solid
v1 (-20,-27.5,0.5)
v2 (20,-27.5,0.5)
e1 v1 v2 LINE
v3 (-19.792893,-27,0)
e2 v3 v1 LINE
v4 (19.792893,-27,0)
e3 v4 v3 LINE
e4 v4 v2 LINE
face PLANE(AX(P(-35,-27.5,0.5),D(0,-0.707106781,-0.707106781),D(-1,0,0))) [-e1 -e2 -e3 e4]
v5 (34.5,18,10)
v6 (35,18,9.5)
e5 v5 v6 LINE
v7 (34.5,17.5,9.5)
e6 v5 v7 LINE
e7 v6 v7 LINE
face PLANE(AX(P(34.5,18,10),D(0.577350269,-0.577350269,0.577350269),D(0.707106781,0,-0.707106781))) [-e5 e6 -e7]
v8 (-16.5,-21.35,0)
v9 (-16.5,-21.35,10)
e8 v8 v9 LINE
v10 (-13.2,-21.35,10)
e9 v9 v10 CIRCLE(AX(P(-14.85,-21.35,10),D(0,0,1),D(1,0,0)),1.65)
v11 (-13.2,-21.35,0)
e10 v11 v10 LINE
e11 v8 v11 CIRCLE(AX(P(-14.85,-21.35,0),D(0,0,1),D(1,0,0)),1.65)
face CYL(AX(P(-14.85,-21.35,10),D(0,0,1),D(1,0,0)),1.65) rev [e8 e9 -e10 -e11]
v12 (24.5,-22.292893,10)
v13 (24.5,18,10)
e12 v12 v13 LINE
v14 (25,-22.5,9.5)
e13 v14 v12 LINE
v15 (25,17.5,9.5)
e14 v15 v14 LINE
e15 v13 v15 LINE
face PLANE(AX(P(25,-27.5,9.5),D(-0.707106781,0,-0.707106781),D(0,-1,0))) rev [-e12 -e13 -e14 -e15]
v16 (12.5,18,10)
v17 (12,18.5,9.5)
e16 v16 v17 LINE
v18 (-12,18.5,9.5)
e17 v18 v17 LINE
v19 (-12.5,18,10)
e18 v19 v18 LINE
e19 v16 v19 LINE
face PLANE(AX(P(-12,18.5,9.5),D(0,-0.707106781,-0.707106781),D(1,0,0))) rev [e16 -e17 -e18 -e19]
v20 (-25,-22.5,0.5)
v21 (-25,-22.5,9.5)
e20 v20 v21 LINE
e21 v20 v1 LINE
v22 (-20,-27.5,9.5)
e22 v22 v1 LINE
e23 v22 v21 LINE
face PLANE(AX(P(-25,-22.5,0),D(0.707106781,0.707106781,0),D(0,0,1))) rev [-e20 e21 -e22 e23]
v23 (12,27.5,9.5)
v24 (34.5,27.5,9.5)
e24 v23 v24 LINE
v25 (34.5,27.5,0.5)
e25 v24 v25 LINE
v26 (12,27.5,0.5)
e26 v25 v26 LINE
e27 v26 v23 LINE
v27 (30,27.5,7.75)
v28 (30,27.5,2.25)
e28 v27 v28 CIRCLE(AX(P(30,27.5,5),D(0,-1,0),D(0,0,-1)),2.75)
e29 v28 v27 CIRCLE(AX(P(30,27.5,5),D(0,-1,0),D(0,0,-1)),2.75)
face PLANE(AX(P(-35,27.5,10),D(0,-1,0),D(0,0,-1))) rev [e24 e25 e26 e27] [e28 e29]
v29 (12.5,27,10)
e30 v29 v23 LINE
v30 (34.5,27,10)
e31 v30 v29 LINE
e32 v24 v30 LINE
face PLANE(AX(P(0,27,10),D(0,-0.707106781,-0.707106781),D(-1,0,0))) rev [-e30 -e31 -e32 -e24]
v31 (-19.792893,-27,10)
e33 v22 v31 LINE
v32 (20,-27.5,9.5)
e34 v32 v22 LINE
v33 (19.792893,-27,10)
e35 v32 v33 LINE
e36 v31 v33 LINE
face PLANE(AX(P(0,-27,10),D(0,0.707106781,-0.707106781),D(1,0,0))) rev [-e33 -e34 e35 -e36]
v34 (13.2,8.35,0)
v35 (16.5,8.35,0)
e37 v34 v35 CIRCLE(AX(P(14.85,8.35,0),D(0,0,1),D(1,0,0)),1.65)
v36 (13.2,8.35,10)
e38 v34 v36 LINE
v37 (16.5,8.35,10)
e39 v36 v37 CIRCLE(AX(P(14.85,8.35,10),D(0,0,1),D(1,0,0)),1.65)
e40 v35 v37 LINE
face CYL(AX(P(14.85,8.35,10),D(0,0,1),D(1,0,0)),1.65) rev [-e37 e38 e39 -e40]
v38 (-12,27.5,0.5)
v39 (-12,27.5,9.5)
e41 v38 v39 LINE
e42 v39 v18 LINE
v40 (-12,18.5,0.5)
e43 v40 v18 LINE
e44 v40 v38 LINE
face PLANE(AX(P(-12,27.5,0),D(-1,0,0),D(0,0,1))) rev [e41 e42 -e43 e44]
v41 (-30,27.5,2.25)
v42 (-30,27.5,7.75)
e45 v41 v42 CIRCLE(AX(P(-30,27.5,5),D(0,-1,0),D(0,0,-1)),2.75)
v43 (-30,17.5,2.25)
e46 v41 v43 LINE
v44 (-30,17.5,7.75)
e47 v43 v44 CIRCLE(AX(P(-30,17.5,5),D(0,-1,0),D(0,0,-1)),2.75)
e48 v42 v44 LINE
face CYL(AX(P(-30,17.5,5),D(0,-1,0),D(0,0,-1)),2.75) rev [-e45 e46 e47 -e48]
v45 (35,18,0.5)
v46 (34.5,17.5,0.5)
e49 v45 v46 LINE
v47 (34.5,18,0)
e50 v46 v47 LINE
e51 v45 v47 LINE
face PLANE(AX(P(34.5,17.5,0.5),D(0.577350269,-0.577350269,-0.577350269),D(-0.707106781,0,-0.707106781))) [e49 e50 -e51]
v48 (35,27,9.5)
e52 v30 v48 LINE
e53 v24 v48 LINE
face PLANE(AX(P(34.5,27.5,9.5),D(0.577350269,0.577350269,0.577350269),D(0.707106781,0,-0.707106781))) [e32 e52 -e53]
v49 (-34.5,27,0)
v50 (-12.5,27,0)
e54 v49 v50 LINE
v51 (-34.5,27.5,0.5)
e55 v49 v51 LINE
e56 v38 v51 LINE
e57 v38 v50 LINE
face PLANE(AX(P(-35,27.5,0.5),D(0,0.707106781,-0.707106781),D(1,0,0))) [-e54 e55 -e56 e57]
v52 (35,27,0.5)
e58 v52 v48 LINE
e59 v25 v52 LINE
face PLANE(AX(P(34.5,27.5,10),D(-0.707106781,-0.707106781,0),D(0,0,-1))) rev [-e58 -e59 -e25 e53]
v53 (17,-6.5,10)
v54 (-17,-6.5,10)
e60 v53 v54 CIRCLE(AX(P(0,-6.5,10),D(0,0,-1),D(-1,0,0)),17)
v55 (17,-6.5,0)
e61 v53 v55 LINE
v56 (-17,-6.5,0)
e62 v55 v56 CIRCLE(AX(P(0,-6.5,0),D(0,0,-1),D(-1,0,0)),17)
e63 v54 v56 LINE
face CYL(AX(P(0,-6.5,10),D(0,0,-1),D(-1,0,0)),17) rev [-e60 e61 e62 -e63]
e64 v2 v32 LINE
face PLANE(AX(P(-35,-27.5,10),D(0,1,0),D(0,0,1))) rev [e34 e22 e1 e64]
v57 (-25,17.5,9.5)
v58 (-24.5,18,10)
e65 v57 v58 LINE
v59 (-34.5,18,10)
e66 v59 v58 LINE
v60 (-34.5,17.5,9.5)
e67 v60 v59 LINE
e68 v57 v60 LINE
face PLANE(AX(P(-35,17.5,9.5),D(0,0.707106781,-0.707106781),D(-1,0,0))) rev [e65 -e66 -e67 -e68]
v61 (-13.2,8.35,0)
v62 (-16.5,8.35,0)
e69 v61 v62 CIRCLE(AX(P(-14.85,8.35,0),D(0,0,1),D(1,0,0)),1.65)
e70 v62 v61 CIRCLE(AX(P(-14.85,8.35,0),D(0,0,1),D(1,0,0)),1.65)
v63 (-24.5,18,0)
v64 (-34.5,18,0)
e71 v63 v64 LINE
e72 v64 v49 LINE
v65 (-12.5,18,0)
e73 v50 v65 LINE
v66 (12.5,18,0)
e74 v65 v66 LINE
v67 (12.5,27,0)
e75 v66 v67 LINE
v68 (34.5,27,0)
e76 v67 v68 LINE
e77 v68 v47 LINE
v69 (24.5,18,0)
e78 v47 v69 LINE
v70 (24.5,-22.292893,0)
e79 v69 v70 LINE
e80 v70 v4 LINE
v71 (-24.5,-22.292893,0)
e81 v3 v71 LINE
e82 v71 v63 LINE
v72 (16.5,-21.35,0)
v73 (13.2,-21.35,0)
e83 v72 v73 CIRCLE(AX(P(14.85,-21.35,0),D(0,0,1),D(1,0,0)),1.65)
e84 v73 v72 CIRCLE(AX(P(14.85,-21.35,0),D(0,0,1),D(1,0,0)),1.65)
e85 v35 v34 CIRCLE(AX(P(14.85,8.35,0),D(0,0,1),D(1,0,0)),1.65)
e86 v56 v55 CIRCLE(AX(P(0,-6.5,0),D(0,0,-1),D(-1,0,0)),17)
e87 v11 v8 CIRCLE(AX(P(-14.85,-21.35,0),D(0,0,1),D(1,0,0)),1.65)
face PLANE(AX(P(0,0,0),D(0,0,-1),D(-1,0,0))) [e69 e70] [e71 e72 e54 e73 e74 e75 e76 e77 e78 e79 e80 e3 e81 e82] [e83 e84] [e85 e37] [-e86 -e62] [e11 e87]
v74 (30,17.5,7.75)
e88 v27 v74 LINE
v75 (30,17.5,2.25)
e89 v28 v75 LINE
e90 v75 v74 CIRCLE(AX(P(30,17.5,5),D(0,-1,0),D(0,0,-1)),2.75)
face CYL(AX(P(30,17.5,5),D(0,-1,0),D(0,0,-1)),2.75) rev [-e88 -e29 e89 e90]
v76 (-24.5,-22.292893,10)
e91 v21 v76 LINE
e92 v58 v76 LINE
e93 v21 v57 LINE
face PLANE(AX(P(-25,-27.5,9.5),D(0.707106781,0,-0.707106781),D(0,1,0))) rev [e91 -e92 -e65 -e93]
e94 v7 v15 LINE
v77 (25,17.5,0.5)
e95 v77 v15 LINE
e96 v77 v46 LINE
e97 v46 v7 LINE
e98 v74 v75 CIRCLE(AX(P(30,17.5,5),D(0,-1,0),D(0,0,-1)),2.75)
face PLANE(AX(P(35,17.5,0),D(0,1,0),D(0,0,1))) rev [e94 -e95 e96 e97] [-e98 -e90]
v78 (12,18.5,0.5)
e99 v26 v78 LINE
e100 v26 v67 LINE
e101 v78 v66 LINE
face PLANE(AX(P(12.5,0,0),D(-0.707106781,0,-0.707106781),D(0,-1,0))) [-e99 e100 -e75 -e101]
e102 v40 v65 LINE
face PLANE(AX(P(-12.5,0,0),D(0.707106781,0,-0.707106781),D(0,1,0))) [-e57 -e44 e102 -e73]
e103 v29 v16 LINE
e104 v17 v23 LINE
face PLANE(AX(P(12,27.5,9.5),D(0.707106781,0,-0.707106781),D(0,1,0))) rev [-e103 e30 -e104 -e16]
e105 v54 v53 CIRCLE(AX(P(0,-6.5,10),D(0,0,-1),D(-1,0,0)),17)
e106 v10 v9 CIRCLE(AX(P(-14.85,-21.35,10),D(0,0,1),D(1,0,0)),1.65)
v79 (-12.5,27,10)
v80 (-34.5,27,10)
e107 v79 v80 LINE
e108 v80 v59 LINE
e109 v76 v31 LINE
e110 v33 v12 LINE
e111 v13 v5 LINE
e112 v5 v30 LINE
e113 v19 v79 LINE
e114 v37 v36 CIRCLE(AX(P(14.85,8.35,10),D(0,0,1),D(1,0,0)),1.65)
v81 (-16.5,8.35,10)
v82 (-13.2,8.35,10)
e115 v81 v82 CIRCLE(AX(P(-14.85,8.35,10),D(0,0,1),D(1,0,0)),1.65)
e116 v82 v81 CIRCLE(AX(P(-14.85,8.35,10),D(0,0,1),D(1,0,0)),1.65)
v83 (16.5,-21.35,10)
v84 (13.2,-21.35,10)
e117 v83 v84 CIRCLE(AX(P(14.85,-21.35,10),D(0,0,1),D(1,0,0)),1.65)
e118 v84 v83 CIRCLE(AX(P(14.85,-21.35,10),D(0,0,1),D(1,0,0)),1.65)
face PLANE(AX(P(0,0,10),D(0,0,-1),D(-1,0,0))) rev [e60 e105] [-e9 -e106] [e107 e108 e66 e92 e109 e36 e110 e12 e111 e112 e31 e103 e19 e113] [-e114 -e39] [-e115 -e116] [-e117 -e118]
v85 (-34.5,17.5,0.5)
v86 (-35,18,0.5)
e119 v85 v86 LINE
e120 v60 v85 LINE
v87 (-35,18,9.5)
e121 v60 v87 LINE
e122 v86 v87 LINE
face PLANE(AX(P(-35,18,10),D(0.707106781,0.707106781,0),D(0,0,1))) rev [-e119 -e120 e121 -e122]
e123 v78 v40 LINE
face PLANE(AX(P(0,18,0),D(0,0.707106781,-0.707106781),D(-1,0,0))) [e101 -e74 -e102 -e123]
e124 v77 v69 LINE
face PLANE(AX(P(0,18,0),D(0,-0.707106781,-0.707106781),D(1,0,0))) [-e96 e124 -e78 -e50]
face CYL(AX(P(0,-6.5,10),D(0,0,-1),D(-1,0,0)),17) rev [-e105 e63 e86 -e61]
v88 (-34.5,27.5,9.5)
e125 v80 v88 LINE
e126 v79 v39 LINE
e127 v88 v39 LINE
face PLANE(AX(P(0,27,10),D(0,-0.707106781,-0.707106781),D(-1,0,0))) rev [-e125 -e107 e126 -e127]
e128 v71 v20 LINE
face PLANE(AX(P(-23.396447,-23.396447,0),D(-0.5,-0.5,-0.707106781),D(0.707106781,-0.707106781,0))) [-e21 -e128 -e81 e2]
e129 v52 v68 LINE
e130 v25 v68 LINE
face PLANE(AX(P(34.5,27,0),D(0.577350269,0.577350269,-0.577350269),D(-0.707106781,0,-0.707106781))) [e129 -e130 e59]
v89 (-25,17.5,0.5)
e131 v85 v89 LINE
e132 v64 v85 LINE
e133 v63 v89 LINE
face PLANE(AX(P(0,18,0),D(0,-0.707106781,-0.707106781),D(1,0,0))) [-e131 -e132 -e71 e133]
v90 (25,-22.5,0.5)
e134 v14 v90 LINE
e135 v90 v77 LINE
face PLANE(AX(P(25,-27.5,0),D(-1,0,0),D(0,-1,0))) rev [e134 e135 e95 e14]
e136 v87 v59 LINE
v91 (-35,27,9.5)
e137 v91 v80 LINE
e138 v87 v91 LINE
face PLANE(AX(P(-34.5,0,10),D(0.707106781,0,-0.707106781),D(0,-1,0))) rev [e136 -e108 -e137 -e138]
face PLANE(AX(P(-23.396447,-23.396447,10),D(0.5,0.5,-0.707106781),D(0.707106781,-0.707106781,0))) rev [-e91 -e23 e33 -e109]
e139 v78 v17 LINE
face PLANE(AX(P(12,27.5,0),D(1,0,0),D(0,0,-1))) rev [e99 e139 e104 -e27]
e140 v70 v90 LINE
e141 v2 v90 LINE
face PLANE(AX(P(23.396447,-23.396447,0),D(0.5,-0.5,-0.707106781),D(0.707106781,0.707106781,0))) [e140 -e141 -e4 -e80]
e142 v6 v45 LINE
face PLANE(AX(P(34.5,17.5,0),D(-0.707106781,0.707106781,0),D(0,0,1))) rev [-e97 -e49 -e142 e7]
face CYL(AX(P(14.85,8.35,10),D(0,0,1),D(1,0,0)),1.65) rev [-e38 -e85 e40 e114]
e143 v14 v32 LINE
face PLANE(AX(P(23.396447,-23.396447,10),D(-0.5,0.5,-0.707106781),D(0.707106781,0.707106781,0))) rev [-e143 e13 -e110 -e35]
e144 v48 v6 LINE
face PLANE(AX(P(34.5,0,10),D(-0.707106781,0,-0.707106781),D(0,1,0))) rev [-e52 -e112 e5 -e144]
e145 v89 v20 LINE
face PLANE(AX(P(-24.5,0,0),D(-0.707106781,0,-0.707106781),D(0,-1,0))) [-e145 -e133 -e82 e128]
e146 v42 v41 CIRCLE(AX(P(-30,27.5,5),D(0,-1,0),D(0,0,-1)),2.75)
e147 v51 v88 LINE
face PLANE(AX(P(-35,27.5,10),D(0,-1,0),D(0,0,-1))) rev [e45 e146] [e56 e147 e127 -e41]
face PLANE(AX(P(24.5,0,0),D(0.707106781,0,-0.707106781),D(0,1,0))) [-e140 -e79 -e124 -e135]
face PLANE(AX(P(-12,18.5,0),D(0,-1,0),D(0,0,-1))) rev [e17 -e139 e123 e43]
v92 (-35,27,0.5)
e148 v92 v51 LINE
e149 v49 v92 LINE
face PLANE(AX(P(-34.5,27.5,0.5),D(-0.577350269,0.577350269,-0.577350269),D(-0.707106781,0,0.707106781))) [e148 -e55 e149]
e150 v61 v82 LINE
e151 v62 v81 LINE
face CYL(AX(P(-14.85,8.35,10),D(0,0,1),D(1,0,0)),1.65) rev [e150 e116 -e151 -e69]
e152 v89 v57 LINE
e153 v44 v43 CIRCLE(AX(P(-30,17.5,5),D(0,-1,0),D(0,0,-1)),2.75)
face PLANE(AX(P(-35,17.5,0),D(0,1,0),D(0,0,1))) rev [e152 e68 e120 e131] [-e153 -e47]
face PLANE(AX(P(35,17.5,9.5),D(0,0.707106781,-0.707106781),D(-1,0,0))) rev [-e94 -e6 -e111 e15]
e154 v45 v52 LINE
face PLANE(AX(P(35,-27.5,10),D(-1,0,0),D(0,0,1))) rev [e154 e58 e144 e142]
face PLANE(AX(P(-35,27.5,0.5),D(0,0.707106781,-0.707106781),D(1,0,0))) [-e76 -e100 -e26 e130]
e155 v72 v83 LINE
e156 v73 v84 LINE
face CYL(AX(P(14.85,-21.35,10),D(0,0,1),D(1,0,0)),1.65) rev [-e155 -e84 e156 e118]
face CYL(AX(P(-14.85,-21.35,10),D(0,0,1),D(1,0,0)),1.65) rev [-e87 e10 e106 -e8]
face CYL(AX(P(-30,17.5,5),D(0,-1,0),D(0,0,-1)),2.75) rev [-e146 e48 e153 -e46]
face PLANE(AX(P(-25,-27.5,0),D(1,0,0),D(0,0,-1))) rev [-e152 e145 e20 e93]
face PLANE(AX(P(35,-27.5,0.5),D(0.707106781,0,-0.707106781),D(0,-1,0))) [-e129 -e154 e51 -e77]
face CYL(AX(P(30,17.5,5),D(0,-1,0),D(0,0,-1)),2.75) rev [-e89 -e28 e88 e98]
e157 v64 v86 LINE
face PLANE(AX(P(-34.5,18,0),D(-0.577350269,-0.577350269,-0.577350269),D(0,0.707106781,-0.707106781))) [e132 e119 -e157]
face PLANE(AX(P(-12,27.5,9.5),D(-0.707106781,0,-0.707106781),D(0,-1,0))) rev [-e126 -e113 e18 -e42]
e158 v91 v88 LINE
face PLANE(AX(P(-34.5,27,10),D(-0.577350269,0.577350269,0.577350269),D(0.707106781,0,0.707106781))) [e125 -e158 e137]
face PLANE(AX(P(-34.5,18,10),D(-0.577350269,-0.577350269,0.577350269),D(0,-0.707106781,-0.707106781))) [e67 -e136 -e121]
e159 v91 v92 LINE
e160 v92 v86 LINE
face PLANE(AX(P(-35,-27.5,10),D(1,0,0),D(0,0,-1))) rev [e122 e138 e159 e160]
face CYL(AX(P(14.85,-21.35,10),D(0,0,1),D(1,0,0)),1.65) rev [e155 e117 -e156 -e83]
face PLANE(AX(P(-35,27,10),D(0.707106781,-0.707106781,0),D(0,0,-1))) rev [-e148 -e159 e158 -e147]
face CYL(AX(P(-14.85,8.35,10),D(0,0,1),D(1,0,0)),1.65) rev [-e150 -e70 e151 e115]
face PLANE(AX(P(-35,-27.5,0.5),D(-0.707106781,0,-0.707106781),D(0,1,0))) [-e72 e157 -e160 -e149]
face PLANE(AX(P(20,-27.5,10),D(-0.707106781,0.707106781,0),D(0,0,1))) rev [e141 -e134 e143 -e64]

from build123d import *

# Parameters (mm, degrees)
SKETCH_1_W              = 70
SKETCH_1_H              = 55
EXTRUDE_1_DEPTH         = 10
SKETCH_2_W              = 10
SKETCH_2_H              = 45
CUT_EXTRUDE_1_DEPTH     = 46.620718977
SKETCH_3_R              = 17
CUT_EXTRUDE_2_DEPTH     = 46.620718977
HOLE_WIZARD_M4_2_D      = 3.3
HOLE_WIZARD_5_5_5_5_1_D = 5.5
CHAMFER_1_SIZE          = 5
SKETCH_12_W             = 24
SKETCH_12_H             = 9
CUT_EXTRUDE_3_DEPTH     = 46.620718977
CHAMFER_2_SIZE          = 0.5


with BuildPart() as part:
    # 草图1 → 凸台-拉伸1 (new body)
    with BuildSketch(Plane.XY):
        Rectangle(SKETCH_1_W, SKETCH_1_H)
    extrude(amount=EXTRUDE_1_DEPTH)

    # 草图2 → 切除-拉伸1 (cut, through all)
    with BuildSketch(Plane.XY.offset(10)):
        with Locations((-30, -5)):
            Rectangle(SKETCH_2_W, SKETCH_2_H)
        with Locations((30, -5)):
            Rectangle(SKETCH_2_W, SKETCH_2_H)
    extrude(amount=-CUT_EXTRUDE_1_DEPTH, mode=Mode.SUBTRACT)

    # 草图3 → 切除-拉伸2 (cut, through all)
    with BuildSketch(Plane(origin=(0, 0, 0), x_dir=(-1, 0, 0), z_dir=(0, 0, -1))):
        with Locations((0, -6.5)):
            Circle(SKETCH_3_R)
    extrude(amount=-CUT_EXTRUDE_2_DEPTH, mode=Mode.SUBTRACT)

    # M4 螺纹孔2 (through all)
    with Locations(Plane.XY.offset(10)):
        with Locations((14.85, -21.35), (-14.85, -21.35), (-14.85, 8.35), (14.85, 8.35)):
            Hole(HOLE_WIZARD_M4_2_D / 2)

    # Ø5.5 (5.5) 直径孔1 (through all)
    with Locations(Plane(origin=(0, 17.5, 0), x_dir=(-1, 0, 0), z_dir=(0, -1, 0))):
        with Locations((-30, -5), (30, -5)):
            Hole(HOLE_WIZARD_5_5_5_5_1_D / 2)

    # 倒角1
    chamfer_1_edges = [part.edges().sort_by_distance(p)[0] for p in [
        (-25, -27.5, 5),
        (25, -27.5, 5),
    ]]
    chamfer(chamfer_1_edges, length=CHAMFER_1_SIZE)

    # 草图12 → 切除-拉伸3 (cut, through all)
    with BuildSketch(Plane.XY.offset(10)):
        with Locations((0, 23)):
            Rectangle(SKETCH_12_W, SKETCH_12_H)
    extrude(amount=-CUT_EXTRUDE_3_DEPTH, mode=Mode.SUBTRACT)

    # 倒角2
    chamfer_2_edges = [part.edges().sort_by_distance(p)[0] for p in [
        (-35, 22.5, 10),
        (0, 18.5, 10),
        (12, 23, 10),
        (-30, 17.5, 0),
        (-35, 17.5, 5),
        (-30, 17.5, 10),
        (35, 22.5, 0),
        (35, 22.5, 10),
        (25, -2.5, 0),
        (30, 17.5, 0),
        (35, 17.5, 5),
        (30, 17.5, 10),
        (25, -2.5, 10),
        (-35, 22.5, 0),
        (23.5, 27.5, 0),
        (23.5, 27.5, 10),
        (-35, 27.5, 5),
        (35, 27.5, 5),
        (-25, -2.5, 10),
        (-25, -2.5, 0),
        (0, -27.5, 10),
        (22.5, -25, 10),
        (-22.5, -25, 10),
        (0, -27.5, 0),
        (22.5, -25, 0),
        (-22.5, -25, 0),
        (-23.5, 27.5, 0),
        (-23.5, 27.5, 10),
        (-12, 23, 0),
        (12, 23, 0),
        (0, 18.5, 0),
        (-12, 23, 10),
    ]]
    chamfer(chamfer_2_edges, length=CHAMFER_2_SIZE)


solid = part.part
